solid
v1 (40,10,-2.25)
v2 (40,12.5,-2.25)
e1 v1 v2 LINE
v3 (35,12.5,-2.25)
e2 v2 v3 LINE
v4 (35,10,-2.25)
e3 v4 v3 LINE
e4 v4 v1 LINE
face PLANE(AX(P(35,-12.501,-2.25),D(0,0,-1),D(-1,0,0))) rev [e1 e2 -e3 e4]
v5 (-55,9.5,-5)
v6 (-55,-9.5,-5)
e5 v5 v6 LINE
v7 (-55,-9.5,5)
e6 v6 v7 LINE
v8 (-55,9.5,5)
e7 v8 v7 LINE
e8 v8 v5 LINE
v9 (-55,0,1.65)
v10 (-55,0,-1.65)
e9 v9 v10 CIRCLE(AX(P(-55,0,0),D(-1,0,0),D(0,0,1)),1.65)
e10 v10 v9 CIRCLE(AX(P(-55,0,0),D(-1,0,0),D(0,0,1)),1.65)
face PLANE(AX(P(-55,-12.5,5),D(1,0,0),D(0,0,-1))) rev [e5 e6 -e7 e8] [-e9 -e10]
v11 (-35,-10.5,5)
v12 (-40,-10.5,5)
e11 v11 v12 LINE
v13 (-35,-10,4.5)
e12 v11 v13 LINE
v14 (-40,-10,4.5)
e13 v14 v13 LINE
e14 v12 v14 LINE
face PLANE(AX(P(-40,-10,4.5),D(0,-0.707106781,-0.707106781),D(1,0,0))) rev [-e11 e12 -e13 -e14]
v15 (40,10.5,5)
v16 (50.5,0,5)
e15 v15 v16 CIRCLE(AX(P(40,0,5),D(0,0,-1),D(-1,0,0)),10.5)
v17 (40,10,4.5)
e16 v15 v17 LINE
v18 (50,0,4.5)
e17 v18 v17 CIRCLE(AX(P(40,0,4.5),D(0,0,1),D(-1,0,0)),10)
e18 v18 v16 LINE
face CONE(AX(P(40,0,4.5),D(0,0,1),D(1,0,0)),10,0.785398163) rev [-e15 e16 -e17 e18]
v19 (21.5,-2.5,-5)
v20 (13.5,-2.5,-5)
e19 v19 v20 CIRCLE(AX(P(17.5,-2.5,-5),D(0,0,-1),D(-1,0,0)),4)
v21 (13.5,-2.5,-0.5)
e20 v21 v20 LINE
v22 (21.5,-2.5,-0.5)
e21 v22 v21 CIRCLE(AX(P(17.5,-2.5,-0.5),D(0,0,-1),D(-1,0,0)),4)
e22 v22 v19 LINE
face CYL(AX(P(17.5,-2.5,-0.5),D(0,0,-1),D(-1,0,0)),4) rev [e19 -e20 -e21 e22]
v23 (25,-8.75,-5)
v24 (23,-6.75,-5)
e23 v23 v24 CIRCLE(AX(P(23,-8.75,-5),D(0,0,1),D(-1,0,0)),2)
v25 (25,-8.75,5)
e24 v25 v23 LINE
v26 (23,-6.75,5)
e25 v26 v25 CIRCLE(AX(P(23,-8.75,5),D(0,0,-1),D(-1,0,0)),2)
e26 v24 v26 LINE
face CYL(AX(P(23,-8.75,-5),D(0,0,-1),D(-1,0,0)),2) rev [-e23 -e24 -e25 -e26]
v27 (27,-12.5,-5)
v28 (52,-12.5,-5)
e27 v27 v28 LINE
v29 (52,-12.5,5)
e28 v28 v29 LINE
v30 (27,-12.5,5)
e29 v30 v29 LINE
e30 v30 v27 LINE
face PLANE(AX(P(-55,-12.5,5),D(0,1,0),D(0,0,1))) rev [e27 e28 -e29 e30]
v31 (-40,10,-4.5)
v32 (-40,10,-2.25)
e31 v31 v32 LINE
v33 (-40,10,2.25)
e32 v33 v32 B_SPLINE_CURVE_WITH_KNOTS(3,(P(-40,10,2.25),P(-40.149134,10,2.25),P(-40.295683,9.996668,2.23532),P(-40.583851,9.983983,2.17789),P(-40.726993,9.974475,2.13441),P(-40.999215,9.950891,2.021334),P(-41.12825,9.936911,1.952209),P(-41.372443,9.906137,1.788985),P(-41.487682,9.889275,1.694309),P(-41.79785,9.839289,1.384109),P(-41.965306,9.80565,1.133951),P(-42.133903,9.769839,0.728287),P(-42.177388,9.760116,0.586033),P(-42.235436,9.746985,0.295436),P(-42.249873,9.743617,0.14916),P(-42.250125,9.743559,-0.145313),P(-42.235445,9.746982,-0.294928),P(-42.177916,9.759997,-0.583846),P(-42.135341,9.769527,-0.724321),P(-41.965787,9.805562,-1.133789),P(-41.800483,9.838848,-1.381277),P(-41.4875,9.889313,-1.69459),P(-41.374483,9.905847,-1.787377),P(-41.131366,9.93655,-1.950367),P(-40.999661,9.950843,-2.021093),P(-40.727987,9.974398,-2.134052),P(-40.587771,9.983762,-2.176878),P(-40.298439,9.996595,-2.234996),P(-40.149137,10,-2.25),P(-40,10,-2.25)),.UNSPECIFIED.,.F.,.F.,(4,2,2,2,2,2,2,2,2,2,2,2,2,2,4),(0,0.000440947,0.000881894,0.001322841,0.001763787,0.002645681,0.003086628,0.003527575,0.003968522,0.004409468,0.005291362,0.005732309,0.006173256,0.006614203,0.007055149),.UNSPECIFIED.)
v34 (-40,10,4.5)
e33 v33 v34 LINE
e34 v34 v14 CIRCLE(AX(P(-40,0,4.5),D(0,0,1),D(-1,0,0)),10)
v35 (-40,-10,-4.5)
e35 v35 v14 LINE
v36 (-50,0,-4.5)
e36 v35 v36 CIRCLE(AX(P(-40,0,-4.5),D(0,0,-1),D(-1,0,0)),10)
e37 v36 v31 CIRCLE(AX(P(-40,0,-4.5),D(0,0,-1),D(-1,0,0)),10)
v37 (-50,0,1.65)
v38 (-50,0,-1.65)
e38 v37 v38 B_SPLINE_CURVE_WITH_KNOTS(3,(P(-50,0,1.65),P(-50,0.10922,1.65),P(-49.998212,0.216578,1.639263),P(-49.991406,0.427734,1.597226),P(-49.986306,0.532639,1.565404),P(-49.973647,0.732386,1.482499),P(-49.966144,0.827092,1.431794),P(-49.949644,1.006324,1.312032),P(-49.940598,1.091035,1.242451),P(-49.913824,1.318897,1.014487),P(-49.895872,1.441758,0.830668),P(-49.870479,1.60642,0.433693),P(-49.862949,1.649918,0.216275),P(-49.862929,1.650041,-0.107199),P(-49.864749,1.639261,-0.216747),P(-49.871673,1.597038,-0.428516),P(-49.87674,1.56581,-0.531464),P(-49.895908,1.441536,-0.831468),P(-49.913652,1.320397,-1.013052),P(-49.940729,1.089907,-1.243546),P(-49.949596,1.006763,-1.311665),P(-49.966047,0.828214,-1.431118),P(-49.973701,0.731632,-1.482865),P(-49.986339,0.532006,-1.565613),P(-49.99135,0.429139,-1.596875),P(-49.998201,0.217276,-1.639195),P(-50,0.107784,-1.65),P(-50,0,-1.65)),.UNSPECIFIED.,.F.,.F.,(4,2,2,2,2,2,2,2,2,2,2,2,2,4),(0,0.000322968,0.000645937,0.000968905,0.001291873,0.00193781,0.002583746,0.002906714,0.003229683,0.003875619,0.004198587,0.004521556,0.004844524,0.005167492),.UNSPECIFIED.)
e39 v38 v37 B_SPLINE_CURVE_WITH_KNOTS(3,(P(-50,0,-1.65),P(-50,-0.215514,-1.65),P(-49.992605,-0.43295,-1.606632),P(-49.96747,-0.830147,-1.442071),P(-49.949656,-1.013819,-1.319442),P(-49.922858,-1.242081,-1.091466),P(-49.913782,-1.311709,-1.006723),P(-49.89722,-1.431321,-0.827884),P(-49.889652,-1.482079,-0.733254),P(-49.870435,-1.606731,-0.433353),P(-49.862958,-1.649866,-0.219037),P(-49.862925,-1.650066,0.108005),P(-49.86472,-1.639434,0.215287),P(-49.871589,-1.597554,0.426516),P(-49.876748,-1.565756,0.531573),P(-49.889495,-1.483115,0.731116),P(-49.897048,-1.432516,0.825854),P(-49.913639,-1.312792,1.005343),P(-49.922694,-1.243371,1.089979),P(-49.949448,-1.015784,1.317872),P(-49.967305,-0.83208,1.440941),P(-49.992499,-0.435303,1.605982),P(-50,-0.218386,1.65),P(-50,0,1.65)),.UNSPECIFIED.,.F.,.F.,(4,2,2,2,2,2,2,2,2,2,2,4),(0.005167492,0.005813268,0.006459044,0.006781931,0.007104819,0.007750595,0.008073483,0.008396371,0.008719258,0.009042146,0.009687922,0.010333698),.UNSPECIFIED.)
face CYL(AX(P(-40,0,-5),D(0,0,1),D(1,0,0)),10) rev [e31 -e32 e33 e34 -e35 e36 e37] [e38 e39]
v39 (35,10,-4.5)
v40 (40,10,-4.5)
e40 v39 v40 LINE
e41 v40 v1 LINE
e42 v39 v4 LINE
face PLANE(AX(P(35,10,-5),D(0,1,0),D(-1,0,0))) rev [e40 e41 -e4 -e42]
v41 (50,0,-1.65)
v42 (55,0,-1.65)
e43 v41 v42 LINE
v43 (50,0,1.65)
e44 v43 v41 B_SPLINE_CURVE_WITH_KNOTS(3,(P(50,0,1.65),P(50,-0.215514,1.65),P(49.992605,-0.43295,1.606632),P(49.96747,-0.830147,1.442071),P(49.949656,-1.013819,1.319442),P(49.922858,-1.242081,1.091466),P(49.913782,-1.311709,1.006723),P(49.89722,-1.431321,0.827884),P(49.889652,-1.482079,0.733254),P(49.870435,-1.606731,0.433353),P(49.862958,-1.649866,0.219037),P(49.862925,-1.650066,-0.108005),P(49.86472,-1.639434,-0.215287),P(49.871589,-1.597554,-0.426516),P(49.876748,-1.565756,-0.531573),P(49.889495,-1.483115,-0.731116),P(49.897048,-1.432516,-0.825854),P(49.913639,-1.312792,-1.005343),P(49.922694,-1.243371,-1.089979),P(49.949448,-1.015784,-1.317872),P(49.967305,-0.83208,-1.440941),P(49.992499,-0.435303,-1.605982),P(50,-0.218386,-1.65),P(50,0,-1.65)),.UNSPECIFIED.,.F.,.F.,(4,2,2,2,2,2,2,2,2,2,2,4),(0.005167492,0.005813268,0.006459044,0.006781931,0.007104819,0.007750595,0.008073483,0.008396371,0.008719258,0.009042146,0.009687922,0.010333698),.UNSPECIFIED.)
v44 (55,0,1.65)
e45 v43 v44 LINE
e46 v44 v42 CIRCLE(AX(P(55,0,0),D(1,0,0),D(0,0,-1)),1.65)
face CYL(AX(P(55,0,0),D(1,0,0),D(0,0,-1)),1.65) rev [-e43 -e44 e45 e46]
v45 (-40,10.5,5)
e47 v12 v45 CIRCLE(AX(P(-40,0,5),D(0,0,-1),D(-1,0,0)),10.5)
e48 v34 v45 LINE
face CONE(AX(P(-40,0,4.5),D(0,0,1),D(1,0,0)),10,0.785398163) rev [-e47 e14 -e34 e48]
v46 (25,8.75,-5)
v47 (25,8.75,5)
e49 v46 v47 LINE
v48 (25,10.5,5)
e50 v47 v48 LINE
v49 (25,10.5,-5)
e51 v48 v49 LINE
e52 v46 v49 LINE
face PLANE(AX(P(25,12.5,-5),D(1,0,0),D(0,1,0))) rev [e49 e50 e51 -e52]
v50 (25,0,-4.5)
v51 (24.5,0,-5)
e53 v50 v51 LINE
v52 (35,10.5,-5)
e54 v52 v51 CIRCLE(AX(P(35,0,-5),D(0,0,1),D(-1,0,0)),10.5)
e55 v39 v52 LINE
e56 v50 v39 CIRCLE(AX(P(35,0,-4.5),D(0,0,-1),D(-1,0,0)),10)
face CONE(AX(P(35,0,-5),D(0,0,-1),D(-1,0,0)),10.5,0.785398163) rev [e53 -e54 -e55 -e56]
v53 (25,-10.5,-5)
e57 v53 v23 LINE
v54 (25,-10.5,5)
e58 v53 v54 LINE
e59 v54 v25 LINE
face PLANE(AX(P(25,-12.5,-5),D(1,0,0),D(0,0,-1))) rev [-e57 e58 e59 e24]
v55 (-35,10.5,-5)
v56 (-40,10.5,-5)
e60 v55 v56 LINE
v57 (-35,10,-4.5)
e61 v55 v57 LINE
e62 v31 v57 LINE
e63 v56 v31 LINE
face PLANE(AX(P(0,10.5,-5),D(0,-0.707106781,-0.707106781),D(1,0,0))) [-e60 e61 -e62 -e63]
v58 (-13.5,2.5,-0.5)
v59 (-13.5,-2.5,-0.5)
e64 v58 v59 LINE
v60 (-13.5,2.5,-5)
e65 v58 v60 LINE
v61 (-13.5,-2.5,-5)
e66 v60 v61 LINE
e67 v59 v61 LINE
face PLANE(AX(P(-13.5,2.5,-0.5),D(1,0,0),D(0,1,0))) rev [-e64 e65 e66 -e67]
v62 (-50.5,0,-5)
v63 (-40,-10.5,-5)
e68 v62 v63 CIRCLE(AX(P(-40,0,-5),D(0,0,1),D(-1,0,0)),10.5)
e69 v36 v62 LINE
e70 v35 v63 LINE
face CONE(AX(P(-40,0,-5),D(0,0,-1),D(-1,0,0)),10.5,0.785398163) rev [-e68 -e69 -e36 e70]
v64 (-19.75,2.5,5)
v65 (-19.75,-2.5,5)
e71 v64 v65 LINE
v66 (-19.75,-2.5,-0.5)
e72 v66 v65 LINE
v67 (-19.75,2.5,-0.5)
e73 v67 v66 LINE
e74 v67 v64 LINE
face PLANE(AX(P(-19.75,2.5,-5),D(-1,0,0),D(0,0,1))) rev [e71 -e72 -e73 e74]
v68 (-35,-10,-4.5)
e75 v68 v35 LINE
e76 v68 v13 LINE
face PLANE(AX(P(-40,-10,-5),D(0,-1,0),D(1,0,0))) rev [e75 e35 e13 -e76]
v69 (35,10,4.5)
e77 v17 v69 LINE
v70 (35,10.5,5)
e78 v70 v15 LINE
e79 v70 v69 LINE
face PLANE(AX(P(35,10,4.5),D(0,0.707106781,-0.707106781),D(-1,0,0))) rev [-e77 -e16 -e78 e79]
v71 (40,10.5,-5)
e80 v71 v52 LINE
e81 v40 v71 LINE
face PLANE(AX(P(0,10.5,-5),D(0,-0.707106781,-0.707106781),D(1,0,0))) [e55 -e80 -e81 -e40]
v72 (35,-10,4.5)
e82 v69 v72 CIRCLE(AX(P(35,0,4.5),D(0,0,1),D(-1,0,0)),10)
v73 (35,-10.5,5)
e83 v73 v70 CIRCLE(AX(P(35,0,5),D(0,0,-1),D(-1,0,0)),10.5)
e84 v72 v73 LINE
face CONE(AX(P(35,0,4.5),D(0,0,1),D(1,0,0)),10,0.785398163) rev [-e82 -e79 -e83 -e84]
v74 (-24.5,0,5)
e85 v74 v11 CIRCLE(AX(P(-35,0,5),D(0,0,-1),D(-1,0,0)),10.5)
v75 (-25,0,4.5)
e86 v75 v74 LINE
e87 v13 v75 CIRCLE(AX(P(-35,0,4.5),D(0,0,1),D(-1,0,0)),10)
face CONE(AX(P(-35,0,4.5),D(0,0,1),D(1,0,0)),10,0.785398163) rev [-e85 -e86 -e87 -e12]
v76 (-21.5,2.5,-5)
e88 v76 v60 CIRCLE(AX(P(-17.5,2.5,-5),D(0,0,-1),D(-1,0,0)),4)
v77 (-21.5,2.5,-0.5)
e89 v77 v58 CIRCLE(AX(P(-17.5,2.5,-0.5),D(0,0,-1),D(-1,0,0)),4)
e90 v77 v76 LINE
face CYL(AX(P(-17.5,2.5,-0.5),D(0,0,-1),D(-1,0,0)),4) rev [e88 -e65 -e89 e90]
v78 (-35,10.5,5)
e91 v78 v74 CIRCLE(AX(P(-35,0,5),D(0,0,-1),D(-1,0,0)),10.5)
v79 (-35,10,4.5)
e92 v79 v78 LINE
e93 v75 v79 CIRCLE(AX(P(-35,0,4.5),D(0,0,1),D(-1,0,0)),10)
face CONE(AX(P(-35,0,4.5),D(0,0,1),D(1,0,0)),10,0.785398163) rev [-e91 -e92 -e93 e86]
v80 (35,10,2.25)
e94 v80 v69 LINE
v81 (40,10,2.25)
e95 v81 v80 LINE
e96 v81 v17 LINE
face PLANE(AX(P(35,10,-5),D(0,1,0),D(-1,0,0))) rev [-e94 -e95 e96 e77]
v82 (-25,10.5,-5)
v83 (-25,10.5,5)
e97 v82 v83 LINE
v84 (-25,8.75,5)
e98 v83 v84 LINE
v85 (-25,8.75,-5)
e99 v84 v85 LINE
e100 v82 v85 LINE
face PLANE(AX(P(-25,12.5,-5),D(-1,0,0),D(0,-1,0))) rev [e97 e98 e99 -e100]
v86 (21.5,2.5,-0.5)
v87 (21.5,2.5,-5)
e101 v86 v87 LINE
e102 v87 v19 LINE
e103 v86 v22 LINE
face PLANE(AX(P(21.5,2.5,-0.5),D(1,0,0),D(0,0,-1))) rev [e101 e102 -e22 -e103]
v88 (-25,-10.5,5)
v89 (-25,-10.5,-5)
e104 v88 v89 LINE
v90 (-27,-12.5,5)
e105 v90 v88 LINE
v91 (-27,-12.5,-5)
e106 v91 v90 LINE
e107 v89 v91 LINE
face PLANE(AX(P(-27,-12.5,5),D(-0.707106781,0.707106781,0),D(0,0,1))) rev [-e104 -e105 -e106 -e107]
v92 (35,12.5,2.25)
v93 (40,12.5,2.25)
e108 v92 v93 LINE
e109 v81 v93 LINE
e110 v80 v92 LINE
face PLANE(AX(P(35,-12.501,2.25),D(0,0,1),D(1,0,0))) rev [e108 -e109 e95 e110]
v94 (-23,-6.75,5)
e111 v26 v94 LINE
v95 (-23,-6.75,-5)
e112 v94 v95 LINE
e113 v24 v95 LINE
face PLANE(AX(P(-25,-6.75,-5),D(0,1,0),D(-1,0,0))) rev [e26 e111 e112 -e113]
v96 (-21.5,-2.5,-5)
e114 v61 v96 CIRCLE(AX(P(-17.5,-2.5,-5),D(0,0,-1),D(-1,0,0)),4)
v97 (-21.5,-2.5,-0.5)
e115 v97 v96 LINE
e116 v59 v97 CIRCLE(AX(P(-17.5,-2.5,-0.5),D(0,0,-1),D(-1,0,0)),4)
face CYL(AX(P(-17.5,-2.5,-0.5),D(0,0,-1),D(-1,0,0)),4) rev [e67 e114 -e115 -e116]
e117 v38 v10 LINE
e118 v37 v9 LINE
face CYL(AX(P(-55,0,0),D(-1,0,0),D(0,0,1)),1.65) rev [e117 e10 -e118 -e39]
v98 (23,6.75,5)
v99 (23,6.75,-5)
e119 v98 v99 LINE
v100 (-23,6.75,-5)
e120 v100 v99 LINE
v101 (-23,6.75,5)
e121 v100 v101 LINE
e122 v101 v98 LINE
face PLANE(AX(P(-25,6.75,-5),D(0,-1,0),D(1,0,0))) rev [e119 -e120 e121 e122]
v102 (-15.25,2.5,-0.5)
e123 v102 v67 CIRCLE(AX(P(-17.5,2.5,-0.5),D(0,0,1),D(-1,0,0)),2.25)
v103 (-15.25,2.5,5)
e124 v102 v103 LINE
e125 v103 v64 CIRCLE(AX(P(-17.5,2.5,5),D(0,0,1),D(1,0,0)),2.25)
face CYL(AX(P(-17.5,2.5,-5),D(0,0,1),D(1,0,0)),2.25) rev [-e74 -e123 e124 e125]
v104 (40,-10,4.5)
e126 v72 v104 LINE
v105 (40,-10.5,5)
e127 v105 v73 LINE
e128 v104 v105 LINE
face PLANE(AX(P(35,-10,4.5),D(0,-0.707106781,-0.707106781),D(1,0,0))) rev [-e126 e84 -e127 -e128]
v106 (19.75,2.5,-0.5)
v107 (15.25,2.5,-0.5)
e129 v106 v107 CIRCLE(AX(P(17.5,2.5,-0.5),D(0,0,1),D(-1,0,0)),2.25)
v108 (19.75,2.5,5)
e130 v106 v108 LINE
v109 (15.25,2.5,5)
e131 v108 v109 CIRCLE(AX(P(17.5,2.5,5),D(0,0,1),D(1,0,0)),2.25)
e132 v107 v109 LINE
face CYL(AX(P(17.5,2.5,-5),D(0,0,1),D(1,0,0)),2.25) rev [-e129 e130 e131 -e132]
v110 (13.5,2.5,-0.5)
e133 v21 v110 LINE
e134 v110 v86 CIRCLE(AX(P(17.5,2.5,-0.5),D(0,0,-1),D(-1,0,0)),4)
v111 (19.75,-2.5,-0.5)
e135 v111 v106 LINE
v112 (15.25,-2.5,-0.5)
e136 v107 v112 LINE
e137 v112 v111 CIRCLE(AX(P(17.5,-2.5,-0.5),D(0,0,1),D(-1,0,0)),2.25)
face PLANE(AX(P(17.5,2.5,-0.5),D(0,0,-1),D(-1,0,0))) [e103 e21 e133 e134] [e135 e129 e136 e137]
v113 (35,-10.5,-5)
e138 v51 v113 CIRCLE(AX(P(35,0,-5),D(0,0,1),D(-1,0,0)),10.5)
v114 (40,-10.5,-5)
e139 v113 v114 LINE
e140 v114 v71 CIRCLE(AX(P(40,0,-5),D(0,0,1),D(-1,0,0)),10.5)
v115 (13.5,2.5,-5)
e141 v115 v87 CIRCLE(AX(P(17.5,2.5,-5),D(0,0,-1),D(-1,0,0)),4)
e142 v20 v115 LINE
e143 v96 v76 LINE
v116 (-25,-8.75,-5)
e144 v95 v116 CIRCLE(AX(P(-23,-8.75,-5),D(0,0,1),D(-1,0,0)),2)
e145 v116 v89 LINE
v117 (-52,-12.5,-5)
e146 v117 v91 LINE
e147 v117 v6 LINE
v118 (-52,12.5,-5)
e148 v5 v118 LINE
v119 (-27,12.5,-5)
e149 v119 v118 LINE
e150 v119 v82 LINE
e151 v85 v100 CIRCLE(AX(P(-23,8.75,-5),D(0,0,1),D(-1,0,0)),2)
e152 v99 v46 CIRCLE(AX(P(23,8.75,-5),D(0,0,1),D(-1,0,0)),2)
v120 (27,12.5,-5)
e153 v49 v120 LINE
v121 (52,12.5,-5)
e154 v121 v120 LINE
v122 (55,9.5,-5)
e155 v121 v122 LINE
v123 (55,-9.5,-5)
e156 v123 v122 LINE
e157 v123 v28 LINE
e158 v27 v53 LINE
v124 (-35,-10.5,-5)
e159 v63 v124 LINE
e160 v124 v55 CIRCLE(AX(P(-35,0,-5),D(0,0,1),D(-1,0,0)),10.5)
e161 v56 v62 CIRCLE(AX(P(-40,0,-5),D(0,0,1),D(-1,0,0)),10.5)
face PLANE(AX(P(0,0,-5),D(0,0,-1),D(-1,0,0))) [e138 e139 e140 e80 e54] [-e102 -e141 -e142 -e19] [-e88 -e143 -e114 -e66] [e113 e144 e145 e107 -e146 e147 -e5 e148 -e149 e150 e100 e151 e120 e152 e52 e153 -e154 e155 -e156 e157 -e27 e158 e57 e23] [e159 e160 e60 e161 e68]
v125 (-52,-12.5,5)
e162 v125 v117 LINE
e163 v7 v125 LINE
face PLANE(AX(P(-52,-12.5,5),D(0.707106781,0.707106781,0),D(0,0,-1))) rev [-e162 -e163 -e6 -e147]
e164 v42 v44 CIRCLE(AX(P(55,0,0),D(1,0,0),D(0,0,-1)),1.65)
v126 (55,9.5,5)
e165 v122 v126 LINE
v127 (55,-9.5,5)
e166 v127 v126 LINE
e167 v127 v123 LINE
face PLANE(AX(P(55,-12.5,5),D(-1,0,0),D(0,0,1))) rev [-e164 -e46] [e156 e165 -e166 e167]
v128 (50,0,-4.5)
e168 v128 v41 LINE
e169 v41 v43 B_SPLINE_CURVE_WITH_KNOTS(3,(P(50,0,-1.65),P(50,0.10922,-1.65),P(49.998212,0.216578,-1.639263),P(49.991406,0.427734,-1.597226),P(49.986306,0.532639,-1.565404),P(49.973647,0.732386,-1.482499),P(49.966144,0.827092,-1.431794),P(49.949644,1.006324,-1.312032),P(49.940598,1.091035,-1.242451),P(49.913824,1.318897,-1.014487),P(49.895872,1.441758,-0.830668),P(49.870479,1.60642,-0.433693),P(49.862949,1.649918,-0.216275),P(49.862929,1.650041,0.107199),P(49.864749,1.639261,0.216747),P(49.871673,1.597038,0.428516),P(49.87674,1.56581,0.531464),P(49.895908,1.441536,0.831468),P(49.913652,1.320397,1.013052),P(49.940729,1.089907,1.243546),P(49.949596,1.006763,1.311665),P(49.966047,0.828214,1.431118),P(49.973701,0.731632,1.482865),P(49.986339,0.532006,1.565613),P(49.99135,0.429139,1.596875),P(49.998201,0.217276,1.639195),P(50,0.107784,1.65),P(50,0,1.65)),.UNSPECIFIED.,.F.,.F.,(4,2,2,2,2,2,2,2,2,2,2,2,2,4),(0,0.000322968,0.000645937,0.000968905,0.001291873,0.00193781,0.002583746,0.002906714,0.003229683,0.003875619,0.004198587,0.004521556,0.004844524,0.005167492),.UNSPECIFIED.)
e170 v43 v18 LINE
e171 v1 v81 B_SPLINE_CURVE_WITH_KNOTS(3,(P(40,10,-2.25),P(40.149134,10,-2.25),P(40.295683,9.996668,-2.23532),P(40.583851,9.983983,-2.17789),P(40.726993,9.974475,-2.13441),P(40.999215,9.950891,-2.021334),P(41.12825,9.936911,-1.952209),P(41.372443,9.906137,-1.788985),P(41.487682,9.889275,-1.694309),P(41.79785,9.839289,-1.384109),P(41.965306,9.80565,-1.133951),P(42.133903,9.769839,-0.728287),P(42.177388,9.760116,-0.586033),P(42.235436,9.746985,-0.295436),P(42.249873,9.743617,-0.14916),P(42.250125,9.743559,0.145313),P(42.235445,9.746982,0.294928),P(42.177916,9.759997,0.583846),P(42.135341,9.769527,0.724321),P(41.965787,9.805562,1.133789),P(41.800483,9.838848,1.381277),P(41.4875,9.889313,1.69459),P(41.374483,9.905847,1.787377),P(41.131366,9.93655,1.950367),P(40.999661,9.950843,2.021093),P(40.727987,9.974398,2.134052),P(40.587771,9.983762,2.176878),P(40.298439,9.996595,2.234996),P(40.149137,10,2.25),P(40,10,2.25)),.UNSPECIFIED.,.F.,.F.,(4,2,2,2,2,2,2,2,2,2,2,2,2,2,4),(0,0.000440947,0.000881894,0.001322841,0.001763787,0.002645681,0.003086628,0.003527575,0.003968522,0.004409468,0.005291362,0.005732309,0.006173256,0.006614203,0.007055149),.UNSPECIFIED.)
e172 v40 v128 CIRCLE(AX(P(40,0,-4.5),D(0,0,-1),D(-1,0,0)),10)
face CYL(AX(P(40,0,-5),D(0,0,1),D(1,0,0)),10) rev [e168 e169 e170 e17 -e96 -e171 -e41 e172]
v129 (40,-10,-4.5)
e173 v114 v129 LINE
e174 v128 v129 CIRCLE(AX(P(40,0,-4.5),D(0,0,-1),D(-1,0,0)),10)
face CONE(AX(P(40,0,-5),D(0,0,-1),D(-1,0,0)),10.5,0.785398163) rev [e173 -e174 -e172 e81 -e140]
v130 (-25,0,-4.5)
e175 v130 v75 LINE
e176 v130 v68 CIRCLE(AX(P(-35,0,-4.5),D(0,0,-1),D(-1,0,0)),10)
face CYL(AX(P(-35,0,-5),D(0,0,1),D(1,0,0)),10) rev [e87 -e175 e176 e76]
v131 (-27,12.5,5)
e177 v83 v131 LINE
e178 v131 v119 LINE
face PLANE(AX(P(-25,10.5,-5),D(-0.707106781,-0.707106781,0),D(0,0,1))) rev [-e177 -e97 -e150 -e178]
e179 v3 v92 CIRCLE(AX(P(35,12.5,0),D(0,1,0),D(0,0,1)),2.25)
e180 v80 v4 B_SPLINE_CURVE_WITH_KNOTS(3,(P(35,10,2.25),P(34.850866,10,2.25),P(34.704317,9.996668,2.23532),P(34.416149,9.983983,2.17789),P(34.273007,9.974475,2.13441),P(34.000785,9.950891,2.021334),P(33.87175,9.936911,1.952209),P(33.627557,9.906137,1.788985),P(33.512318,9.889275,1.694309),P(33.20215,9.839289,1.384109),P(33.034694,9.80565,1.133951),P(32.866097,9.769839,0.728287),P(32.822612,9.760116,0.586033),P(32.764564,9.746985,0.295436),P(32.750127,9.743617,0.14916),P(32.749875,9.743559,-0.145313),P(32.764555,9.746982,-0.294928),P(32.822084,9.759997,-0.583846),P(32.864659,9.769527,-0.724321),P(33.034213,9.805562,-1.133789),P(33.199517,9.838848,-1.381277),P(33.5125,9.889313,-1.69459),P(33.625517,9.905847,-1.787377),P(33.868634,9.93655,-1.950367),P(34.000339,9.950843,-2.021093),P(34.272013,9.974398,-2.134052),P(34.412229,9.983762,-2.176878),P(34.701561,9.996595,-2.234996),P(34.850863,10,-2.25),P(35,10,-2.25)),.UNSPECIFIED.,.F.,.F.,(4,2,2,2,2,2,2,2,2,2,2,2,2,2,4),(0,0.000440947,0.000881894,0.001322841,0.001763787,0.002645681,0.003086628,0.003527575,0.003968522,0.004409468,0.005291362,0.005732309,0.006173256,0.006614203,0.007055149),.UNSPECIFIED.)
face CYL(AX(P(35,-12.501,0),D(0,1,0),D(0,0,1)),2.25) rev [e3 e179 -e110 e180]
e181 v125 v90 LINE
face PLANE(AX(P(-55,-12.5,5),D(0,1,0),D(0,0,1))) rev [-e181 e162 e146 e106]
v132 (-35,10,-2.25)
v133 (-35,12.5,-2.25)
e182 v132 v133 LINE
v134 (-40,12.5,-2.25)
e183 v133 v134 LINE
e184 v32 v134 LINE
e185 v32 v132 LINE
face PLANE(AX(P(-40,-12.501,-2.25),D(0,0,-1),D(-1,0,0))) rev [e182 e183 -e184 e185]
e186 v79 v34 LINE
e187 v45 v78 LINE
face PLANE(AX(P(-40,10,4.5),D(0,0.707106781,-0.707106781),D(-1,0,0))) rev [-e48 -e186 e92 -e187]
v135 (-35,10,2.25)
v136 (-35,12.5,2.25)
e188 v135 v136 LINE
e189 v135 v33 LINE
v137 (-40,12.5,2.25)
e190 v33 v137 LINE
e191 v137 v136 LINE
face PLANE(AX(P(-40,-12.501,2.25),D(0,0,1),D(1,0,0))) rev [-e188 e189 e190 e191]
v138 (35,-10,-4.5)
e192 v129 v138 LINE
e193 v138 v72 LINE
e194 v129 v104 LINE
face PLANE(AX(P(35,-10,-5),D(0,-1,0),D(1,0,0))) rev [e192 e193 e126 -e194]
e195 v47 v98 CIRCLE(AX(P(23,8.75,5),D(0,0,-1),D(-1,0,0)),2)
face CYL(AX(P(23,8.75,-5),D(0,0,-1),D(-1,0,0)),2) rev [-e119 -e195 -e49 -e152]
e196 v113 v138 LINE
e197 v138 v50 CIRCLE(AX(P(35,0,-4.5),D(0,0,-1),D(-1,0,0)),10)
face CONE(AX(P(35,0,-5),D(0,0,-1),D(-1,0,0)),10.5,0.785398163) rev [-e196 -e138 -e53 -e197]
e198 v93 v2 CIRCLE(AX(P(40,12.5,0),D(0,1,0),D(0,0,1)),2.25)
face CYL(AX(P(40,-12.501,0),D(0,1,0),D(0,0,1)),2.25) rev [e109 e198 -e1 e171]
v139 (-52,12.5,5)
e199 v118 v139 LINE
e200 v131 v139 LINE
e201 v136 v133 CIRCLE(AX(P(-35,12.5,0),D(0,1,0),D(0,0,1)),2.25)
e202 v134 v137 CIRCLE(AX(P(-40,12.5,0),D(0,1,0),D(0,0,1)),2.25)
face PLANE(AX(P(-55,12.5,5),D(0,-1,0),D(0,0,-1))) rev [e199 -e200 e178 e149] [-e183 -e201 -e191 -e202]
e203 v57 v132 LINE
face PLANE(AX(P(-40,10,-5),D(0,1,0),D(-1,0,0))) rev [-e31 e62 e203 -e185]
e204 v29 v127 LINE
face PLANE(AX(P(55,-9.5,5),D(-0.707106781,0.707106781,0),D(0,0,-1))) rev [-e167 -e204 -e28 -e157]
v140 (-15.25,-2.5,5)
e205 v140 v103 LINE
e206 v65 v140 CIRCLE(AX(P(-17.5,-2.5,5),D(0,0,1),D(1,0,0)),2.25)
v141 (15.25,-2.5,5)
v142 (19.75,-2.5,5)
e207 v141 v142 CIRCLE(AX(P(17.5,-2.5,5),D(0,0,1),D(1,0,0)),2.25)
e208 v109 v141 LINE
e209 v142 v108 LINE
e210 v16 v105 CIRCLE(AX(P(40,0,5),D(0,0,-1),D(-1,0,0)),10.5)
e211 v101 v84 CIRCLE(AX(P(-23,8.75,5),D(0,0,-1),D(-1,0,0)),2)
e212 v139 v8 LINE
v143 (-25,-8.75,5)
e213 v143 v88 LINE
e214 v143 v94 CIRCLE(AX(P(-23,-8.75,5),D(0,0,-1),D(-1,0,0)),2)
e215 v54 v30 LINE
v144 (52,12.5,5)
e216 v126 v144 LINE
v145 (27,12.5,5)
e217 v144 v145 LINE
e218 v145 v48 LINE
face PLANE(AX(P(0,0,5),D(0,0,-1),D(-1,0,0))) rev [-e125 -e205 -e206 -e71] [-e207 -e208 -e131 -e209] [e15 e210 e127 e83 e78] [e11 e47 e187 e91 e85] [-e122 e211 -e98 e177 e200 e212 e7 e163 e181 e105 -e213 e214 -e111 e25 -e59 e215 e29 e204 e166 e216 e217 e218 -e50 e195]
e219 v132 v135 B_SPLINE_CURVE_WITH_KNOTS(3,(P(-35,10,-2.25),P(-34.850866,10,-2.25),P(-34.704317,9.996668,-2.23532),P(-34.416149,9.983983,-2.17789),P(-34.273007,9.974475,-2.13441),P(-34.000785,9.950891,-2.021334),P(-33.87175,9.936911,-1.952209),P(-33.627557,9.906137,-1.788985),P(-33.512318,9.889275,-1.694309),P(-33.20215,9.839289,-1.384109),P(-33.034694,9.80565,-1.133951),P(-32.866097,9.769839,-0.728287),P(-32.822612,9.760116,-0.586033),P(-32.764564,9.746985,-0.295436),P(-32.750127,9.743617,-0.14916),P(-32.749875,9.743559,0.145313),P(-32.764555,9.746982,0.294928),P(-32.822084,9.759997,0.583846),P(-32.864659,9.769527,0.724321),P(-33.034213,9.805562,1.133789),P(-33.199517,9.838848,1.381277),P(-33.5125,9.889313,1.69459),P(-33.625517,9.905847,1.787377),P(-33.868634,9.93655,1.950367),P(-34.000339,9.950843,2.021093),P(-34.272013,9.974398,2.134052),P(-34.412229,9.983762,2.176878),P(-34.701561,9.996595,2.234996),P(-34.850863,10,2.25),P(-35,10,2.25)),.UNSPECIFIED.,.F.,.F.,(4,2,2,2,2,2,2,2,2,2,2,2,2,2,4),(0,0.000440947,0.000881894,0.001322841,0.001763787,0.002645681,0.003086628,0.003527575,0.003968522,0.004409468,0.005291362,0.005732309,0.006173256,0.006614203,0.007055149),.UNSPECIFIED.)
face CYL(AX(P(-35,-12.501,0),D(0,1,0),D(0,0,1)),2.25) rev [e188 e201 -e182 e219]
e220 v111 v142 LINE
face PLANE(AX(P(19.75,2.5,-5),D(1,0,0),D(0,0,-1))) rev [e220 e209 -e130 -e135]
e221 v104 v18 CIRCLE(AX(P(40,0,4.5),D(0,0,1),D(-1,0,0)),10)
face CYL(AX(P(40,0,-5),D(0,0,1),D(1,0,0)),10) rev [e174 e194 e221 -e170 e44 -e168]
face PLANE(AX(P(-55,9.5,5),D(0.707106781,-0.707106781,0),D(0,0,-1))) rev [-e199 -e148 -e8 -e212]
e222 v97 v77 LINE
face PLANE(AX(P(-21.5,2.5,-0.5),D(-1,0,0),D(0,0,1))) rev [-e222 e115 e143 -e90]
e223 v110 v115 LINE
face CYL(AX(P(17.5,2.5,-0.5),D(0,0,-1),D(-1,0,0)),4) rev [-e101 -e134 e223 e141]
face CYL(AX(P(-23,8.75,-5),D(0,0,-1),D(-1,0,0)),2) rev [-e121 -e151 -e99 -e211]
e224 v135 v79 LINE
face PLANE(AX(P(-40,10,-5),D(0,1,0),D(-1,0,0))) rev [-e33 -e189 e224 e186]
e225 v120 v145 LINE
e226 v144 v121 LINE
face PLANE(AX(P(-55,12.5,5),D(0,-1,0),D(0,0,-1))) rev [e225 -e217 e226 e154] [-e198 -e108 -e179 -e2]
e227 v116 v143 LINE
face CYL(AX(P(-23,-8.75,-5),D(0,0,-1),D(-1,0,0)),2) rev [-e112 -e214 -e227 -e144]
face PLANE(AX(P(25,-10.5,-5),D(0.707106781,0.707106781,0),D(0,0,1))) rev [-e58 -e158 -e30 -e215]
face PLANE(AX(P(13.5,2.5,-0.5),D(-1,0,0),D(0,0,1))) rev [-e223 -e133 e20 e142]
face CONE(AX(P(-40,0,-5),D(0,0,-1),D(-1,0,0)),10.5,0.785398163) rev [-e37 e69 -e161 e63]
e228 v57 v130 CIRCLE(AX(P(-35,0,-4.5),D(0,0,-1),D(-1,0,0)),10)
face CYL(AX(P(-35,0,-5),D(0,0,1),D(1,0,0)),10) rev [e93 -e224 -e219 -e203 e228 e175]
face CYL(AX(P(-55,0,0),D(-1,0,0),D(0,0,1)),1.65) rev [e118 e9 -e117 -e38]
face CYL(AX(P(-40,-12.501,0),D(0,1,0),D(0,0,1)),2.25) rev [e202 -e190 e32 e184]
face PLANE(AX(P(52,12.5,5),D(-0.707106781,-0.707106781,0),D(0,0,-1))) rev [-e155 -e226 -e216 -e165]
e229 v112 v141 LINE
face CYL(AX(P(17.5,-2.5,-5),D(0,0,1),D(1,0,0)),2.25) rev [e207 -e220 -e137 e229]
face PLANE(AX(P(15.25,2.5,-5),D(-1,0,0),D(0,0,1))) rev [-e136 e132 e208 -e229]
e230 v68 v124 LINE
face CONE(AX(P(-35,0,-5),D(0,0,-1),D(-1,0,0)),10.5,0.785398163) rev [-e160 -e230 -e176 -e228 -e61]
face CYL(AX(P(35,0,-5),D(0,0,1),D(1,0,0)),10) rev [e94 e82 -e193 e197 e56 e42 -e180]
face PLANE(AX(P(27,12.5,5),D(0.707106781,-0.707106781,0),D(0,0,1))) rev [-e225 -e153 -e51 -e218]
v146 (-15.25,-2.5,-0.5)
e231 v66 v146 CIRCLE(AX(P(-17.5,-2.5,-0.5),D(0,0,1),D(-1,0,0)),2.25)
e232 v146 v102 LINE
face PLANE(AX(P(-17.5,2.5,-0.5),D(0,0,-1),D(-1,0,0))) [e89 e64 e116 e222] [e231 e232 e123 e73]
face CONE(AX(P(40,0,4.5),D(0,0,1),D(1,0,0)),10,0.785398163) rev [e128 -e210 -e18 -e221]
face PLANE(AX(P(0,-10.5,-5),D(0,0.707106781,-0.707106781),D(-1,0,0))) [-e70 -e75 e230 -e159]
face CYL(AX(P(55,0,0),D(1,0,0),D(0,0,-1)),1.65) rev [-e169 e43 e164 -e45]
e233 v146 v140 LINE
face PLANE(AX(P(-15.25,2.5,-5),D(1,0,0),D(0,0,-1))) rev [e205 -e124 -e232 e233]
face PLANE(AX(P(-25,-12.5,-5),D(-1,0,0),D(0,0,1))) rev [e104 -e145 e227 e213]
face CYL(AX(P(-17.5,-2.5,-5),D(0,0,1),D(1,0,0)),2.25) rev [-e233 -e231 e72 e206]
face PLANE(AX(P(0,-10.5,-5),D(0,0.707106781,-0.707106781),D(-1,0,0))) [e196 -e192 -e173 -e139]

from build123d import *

# Parameters (mm, degrees)
SKETCH1_W              = 110
SKETCH1_H              = 25
BOSS_EXTRUDE1_DEPTH    = 5
CUT_EXTRUDE1_DEPTH     = 58.282196187
CHAMFER1_SIZE          = 3
CHAMFER2_SIZE          = 0.5
CUT_EXTRUDE2_DEPTH     = 58.282196187
CUT_EXTRUDE3_REACH     = 62.622
M4_TAPPED_HOLE1_REACH  = 112.821
M4_TAPPED_HOLE1_BORE_R = 1.65
M4_TAPPED_HOLE2_REACH  = 112.821
M4_TAPPED_HOLE2_BORE_R = 1.65
CUT_EXTRUDE4_DEPTH     = 4.5
SKETCH12_W             = 50
SKETCH12_H             = 5.75
CUT_EXTRUDE5_DEPTH     = 58.282196305
FILLET1_R              = 2
CHAMFER3_SIZE          = 2


with BuildPart() as part:
    # Sketch1 → Boss-Extrude1 (new, symmetric)
    with BuildSketch(Plane.XY):
        Rectangle(SKETCH1_W, SKETCH1_H)
    extrude(amount=BOSS_EXTRUDE1_DEPTH, both=True)

    # Sketch2 → Cut-Extrude1 (cut, through all)
    with BuildSketch(Plane.XY.offset(5)):
        with BuildLine():
            Line((35, 10), (40, 10))
            ThreePointArc((40, 10), (50, 0), (40, -10))
            Line((40, -10), (35, -10))
            ThreePointArc((35, -10), (25, 0), (35, 10))
        make_face()
        with BuildLine():
            Line((-40, 10), (-35, 10))
            ThreePointArc((-35, 10), (-25, 0), (-35, -10))
            Line((-35, -10), (-40, -10))
            ThreePointArc((-40, -10), (-50, 0), (-40, 10))
        make_face()
    extrude(amount=-CUT_EXTRUDE1_DEPTH, mode=Mode.SUBTRACT)

    # Chamfer1
    chamfer1_edges = [part.edges().sort_by_distance(p)[0] for p in [
        (55, -12.5, 0),
        (-55, -12.5, 0),
        (-55, 12.5, 0),
        (55, 12.5, 0),
    ]]
    chamfer(chamfer1_edges, length=CHAMFER1_SIZE)

    # Chamfer2
    chamfer2_edges = [part.edges().sort_by_distance(p)[0] for p in [
        (25, 0, -5),
        (37.5, 10, -5),
        (50, 0, -5),
        (37.5, -10, -5),
        (25, 0, 5),
        (37.5, -10, 5),
        (50, 0, 5),
        (37.5, 10, 5),
        (-50, 0, -5),
        (-37.5, 10, -5),
        (-25, 0, -5),
        (-37.5, -10, -5),
        (-50, 0, 5),
        (-37.5, -10, 5),
        (-25, 0, 5),
        (-37.5, 10, 5),
    ]]
    chamfer(chamfer2_edges, length=CHAMFER2_SIZE)

    # Sketch3 → Cut-Extrude2 (cut, through all)
    with BuildSketch(Plane.XY.offset(5)):
        with BuildLine():
            Line((19.75, 2.5), (19.75, -2.5))
            ThreePointArc((19.75, -2.5), (17.5, -4.75), (15.25, -2.5))
            Line((15.25, -2.5), (15.25, 2.5))
            ThreePointArc((15.25, 2.5), (17.5, 4.75), (19.75, 2.5))
        make_face()
        with BuildLine():
            Line((-15.25, 2.5), (-15.25, -2.5))
            ThreePointArc((-15.25, -2.5), (-17.5, -4.75), (-19.75, -2.5))
            Line((-19.75, -2.5), (-19.75, 2.5))
            ThreePointArc((-19.75, 2.5), (-17.5, 4.75), (-15.25, 2.5))
        make_face()
    extrude(amount=-CUT_EXTRUDE2_DEPTH, mode=Mode.SUBTRACT)

    # Sketch6 → Cut-Extrude3 (cut, up to next)
    with BuildSketch(Plane(origin=(0, 12.5, 0), x_dir=(1, 0, 0), z_dir=(0, 1, 0)), mode=Mode.PRIVATE) as cut_extrude3_sk1:
        with BuildLine():
            Line((-40, 2.25), (-35, 2.25))
            ThreePointArc((-35, 2.25), (-32.75, 0), (-35, -2.25))
            Line((-35, -2.25), (-40, -2.25))
            ThreePointArc((-40, -2.25), (-42.25, 0), (-40, 2.25))
        make_face()
    cut_extrude3_tool1 = extrude(cut_extrude3_sk1.sketch, amount=-CUT_EXTRUDE3_REACH, mode=Mode.PRIVATE) & part.part
    # Sketch6 → Cut-Extrude3 (cut, up to next)
    with BuildSketch(Plane(origin=(0, 12.5, 0), x_dir=(1, 0, 0), z_dir=(0, 1, 0)), mode=Mode.PRIVATE) as cut_extrude3_sk2:
        with BuildLine():
            Line((35, 2.25), (40, 2.25))
            ThreePointArc((40, 2.25), (42.25, 0), (40, -2.25))
            Line((40, -2.25), (35, -2.25))
            ThreePointArc((35, -2.25), (32.75, 0), (35, 2.25))
        make_face()
    cut_extrude3_tool2 = extrude(cut_extrude3_sk2.sketch, amount=-CUT_EXTRUDE3_REACH, mode=Mode.PRIVATE) & part.part
    add(cut_extrude3_tool1.solids().sort_by_distance((-37.5, 12.5, 0))[0], mode=Mode.SUBTRACT)
    add(cut_extrude3_tool2.solids().sort_by_distance((37.5, 12.5, 0))[0], mode=Mode.SUBTRACT)

    # M4 Tapped Hole1 bore → M4 Tapped Hole1 (cut, up to next)
    with BuildSketch(Plane(origin=(55, 0, 0), x_dir=(0, 0, -1), z_dir=(1, 0, 0)), mode=Mode.PRIVATE) as m4_tapped_hole1_sk1:
        Circle(M4_TAPPED_HOLE1_BORE_R)
    m4_tapped_hole1_tool1 = extrude(m4_tapped_hole1_sk1.sketch, amount=-M4_TAPPED_HOLE1_REACH, mode=Mode.PRIVATE) & part.part
    add(m4_tapped_hole1_tool1.solids().sort_by_distance((55, 0, 0))[0], mode=Mode.SUBTRACT)

    # M4 Tapped Hole2 bore → M4 Tapped Hole2 (cut, up to next)
    with BuildSketch(Plane.ZY.offset(55), mode=Mode.PRIVATE) as m4_tapped_hole2_sk1:
        Circle(M4_TAPPED_HOLE2_BORE_R)
    m4_tapped_hole2_tool1 = extrude(m4_tapped_hole2_sk1.sketch, amount=-M4_TAPPED_HOLE2_REACH, mode=Mode.PRIVATE) & part.part
    add(m4_tapped_hole2_tool1.solids().sort_by_distance((-55, 0, 0))[0], mode=Mode.SUBTRACT)

    # Sketch11 → Cut-Extrude4 (cut)
    with BuildSketch(Plane(origin=(0, 0, -5), x_dir=(-1, 0, 0), z_dir=(0, 0, -1))):
        with BuildLine():
            Line((-13.5, 2.5), (-13.5, -2.5))
            ThreePointArc((-13.5, -2.5), (-17.5, -6.5), (-21.5, -2.5))
            Line((-21.5, -2.5), (-21.5, 2.5))
            ThreePointArc((-21.5, 2.5), (-17.5, 6.5), (-13.5, 2.5))
        make_face()
        with BuildLine():
            Line((21.5, 2.5), (21.5, -2.5))
            ThreePointArc((21.5, -2.5), (17.5, -6.5), (13.5, -2.5))
            Line((13.5, -2.5), (13.5, 2.5))
            ThreePointArc((13.5, 2.5), (17.5, 6.5), (21.5, 2.5))
        make_face()
    extrude(amount=-CUT_EXTRUDE4_DEPTH, mode=Mode.SUBTRACT)

    # Sketch12 → Cut-Extrude5 (cut, through all)
    with BuildSketch(Plane.XY.offset(5)):
        with Locations((0, -9.625)):
            Rectangle(SKETCH12_W, SKETCH12_H)
        with Locations((0, 9.625)):
            Rectangle(SKETCH12_W, SKETCH12_H)
    extrude(amount=-CUT_EXTRUDE5_DEPTH, mode=Mode.SUBTRACT)

    # Fillet1
    fillet1_edges = [part.edges().sort_by_distance(p)[0] for p in [
        (-25, -6.75, 0),
        (25, -6.75, 0),
        (-25, 6.75, 0),
        (25, 6.75, 0),
    ]]
    fillet(fillet1_edges, radius=FILLET1_R)

    # Chamfer3
    chamfer3_edges = [part.edges().sort_by_distance(p)[0] for p in [
        (-25, -12.5, 0),
        (25, -12.5, 0),
        (-25, 12.5, 0),
        (25, 12.5, 0),
    ]]
    chamfer(chamfer3_edges, length=CHAMFER3_SIZE)


solid = part.part
